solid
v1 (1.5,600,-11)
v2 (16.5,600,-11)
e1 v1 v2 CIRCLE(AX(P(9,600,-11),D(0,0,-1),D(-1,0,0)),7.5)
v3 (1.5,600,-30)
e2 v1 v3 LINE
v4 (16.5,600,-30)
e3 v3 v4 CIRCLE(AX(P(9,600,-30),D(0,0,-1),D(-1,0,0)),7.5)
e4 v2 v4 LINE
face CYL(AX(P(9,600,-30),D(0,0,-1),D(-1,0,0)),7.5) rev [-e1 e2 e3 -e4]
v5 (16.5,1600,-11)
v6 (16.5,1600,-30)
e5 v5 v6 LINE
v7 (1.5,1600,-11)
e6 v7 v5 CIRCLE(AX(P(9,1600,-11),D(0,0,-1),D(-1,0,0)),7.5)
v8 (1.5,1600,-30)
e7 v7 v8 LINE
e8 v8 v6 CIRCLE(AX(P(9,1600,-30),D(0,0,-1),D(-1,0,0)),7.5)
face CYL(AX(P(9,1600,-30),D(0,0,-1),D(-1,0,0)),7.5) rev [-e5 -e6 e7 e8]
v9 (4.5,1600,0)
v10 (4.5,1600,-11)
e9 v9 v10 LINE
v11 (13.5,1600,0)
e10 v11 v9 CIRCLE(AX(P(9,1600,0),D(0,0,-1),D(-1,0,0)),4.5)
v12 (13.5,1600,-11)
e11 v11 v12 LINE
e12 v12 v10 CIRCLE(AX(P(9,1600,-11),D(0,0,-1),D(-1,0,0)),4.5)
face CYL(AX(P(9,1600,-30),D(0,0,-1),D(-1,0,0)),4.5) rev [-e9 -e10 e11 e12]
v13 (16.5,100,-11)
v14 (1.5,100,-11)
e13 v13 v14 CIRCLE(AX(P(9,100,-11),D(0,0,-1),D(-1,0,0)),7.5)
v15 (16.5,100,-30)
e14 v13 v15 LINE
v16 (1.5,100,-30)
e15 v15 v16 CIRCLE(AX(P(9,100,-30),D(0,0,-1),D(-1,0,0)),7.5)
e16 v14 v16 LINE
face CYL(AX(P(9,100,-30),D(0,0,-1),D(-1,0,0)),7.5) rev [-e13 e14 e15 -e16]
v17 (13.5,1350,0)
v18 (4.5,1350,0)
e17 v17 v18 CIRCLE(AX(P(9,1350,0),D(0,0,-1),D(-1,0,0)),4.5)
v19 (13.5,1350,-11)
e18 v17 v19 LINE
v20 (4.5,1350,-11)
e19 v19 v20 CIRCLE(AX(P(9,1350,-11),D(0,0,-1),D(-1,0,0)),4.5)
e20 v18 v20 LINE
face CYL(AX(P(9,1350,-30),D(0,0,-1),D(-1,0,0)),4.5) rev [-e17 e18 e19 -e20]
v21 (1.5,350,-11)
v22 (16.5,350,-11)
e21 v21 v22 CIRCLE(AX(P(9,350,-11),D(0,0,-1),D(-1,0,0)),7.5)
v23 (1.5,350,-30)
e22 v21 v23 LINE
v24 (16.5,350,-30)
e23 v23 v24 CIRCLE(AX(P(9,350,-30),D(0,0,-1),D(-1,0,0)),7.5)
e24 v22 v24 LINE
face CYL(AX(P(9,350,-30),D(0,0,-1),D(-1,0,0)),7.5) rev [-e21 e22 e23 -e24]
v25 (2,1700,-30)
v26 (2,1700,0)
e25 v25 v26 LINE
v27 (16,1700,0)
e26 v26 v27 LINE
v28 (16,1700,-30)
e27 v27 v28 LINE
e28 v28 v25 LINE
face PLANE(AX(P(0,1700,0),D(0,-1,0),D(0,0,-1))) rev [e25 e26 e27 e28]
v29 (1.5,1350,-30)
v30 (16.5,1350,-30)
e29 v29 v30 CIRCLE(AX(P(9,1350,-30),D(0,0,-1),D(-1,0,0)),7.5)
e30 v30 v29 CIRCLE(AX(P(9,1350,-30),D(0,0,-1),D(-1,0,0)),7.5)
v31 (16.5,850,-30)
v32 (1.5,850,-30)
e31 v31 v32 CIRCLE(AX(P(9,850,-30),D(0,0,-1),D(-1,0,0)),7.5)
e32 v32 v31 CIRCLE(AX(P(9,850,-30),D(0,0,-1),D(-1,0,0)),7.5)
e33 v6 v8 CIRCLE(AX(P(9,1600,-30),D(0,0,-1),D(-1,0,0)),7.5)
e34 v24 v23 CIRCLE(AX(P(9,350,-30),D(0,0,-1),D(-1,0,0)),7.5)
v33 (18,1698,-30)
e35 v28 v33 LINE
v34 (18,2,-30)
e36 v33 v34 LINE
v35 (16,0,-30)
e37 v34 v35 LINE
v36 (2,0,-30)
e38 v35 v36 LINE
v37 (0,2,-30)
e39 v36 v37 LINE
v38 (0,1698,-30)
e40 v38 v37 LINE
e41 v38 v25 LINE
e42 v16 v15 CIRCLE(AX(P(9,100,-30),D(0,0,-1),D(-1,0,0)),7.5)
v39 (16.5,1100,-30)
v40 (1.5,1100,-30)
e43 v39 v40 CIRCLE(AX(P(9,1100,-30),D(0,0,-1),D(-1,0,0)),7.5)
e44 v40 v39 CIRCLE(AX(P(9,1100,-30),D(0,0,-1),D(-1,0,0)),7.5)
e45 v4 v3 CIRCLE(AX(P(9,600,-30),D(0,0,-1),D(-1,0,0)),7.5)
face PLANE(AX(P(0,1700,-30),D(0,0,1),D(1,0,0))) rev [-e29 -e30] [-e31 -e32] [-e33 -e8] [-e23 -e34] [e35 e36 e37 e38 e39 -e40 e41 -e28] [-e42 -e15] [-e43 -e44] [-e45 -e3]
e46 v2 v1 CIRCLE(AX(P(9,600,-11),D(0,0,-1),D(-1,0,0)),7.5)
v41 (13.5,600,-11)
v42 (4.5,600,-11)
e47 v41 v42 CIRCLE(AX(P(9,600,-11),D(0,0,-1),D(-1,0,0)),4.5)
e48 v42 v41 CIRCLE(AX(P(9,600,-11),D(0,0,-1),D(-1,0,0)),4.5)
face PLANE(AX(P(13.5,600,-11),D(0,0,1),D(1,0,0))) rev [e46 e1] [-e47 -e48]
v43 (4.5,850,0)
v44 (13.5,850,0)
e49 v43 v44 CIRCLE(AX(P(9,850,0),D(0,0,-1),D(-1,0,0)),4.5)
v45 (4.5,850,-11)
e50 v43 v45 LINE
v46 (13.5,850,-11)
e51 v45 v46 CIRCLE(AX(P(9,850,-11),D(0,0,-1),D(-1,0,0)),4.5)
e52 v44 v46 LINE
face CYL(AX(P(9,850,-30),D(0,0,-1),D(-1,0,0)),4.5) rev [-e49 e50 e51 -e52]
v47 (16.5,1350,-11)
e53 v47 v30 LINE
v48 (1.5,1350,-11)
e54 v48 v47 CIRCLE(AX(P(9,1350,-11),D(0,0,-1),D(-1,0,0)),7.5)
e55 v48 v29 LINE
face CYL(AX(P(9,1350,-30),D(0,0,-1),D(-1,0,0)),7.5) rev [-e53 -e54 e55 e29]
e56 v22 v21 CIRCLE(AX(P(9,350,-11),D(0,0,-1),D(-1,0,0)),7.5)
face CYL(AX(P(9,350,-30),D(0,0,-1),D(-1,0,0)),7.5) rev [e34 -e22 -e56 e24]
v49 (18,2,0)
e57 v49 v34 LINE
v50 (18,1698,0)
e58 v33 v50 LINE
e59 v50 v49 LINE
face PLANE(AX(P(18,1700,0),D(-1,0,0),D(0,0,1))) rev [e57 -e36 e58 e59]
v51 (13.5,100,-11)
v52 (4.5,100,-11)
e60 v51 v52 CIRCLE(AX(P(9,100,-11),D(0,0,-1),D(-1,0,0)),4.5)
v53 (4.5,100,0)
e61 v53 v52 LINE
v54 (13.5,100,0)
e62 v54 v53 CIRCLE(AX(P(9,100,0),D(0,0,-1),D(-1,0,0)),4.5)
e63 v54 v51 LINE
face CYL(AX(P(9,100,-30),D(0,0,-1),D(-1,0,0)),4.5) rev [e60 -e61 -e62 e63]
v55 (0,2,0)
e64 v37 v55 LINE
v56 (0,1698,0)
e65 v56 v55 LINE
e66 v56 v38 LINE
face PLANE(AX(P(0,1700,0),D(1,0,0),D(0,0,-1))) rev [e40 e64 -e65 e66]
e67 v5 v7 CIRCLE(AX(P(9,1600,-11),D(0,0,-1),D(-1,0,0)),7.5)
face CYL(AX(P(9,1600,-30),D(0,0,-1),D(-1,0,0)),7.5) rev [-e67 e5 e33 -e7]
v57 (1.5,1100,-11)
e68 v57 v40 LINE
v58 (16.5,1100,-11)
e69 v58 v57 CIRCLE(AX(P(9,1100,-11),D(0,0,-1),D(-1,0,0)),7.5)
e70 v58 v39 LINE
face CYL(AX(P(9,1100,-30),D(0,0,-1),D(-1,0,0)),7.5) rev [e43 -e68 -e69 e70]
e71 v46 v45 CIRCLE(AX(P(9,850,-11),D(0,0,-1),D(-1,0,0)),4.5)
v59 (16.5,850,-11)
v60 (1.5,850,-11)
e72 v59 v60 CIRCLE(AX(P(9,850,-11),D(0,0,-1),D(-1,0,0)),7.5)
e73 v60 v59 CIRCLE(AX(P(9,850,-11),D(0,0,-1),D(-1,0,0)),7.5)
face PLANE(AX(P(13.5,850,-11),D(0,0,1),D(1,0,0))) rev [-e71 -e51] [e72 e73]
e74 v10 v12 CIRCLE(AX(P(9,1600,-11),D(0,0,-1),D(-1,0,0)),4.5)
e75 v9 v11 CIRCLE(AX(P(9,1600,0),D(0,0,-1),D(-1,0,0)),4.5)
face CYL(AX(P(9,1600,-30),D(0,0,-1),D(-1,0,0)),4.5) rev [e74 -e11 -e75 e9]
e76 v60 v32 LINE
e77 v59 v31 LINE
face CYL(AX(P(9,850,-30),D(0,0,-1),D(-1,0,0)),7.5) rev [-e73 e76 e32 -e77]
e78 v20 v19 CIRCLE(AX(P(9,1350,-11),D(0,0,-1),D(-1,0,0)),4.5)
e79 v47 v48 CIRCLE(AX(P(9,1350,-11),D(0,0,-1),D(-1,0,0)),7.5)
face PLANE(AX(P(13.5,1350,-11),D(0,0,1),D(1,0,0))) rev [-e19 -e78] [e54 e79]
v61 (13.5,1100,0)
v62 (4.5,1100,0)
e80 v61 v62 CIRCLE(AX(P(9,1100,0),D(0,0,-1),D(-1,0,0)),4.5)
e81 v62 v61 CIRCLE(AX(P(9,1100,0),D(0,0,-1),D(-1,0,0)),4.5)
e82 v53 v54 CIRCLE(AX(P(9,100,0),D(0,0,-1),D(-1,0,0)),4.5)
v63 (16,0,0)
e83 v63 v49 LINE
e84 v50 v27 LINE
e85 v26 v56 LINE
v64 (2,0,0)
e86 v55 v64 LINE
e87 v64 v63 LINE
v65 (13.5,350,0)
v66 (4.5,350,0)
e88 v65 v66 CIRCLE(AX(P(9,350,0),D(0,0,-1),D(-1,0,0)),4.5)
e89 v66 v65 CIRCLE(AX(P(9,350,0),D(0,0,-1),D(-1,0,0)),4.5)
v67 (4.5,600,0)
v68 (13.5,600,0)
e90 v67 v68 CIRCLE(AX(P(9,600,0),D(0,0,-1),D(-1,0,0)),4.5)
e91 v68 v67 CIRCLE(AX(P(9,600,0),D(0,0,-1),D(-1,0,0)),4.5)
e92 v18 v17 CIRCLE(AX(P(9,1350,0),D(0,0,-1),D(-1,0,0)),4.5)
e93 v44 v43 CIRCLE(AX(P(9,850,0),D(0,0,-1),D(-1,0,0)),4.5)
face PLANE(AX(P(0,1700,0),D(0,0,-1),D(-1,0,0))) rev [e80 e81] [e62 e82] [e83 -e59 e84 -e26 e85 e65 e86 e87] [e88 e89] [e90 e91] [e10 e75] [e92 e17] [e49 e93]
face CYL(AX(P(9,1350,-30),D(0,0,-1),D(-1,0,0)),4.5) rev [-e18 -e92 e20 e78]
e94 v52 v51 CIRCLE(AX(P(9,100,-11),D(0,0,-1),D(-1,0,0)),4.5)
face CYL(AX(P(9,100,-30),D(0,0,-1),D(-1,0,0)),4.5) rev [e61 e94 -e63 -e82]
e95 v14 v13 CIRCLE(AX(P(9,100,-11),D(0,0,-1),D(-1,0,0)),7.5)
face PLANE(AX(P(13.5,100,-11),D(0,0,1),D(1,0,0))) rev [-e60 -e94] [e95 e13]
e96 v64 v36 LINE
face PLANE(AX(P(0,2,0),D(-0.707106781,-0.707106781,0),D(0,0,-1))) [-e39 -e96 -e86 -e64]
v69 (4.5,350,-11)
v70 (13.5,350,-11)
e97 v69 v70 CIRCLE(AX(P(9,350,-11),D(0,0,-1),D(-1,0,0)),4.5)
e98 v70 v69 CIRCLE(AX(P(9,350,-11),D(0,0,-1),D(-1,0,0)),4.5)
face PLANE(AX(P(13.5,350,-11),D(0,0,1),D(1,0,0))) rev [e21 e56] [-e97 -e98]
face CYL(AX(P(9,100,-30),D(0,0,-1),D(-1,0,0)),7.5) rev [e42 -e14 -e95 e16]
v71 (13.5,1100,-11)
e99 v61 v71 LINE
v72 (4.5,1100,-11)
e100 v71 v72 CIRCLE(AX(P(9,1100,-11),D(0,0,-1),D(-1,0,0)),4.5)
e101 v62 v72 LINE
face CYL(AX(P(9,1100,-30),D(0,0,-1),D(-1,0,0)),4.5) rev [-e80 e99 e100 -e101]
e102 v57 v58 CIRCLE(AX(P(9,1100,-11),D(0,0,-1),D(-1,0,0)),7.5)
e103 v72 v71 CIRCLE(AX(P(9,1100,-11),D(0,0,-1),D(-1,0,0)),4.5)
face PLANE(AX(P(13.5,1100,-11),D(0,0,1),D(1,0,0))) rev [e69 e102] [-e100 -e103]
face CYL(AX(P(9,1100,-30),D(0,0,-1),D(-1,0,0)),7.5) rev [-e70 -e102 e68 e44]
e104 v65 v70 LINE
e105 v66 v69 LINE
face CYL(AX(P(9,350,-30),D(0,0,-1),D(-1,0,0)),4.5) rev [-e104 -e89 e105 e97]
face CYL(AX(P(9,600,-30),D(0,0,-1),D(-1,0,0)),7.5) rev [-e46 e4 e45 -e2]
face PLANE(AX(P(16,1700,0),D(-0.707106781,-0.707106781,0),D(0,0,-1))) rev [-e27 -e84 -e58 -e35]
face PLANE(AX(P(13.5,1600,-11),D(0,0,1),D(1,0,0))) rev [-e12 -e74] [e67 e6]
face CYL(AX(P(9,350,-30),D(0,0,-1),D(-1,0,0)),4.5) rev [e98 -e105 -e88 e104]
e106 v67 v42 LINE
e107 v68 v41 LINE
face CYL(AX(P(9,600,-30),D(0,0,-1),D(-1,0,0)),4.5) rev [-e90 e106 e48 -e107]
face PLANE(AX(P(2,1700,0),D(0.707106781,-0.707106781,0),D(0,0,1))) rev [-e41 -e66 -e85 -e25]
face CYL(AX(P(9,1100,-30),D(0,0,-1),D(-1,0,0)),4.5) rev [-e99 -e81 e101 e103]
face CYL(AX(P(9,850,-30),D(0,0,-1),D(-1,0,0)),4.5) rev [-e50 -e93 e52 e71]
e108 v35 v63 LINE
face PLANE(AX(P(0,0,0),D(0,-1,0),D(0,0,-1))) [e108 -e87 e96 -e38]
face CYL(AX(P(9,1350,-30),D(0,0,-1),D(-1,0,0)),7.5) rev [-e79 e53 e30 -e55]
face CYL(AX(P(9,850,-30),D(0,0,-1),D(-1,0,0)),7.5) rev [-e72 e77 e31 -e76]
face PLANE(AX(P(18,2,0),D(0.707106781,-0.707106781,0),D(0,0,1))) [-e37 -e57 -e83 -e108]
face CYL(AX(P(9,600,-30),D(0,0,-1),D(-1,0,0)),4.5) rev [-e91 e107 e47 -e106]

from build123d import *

# Parameters (mm, degrees)
SKETCH_1_W                   = 18
SKETCH_1_H                   = 30
EXTRUDE_1_DEPTH              = 1700
CHAMFER_1_SIZE               = 2
HOLE_WIZARD_M8_1_D           = 9
HOLE_WIZARD_M8_1_CBORE_D     = 15
HOLE_WIZARD_M8_1_CBORE_DEPTH = 19


with BuildPart() as part:
    # 草图1 → 凸台-拉伸1 (new body)
    with BuildSketch(Plane(origin=(0, 0, 0), x_dir=(1, 0, 0), z_dir=(0, 1, 0))):
        with Locations((9, 15)):
            Rectangle(SKETCH_1_W, SKETCH_1_H)
    extrude(amount=EXTRUDE_1_DEPTH)

    # 倒角1
    chamfer_1_edges = [part.edges().sort_by_distance(p)[0] for p in [
        (18, 1700, -15),
        (0, 1700, -15),
        (18, 0, -15),
        (0, 0, -15),
    ]]
    chamfer(chamfer_1_edges, length=CHAMFER_1_SIZE)

    # M8 六角圆柱头螺钉的柱形沉头孔1 (through all)
    with Locations(Plane(origin=(0, 0, -30), x_dir=(-1, 0, 0), z_dir=(0, 0, -1))):
        with Locations((-9, 1600), (-9, 1350), (-9, 1100), (-9, 600), (-9, 350), (-9, 100), (-9, 850)):
            CounterBoreHole(HOLE_WIZARD_M8_1_D / 2, HOLE_WIZARD_M8_1_CBORE_D / 2, HOLE_WIZARD_M8_1_CBORE_DEPTH)


solid = part.part
